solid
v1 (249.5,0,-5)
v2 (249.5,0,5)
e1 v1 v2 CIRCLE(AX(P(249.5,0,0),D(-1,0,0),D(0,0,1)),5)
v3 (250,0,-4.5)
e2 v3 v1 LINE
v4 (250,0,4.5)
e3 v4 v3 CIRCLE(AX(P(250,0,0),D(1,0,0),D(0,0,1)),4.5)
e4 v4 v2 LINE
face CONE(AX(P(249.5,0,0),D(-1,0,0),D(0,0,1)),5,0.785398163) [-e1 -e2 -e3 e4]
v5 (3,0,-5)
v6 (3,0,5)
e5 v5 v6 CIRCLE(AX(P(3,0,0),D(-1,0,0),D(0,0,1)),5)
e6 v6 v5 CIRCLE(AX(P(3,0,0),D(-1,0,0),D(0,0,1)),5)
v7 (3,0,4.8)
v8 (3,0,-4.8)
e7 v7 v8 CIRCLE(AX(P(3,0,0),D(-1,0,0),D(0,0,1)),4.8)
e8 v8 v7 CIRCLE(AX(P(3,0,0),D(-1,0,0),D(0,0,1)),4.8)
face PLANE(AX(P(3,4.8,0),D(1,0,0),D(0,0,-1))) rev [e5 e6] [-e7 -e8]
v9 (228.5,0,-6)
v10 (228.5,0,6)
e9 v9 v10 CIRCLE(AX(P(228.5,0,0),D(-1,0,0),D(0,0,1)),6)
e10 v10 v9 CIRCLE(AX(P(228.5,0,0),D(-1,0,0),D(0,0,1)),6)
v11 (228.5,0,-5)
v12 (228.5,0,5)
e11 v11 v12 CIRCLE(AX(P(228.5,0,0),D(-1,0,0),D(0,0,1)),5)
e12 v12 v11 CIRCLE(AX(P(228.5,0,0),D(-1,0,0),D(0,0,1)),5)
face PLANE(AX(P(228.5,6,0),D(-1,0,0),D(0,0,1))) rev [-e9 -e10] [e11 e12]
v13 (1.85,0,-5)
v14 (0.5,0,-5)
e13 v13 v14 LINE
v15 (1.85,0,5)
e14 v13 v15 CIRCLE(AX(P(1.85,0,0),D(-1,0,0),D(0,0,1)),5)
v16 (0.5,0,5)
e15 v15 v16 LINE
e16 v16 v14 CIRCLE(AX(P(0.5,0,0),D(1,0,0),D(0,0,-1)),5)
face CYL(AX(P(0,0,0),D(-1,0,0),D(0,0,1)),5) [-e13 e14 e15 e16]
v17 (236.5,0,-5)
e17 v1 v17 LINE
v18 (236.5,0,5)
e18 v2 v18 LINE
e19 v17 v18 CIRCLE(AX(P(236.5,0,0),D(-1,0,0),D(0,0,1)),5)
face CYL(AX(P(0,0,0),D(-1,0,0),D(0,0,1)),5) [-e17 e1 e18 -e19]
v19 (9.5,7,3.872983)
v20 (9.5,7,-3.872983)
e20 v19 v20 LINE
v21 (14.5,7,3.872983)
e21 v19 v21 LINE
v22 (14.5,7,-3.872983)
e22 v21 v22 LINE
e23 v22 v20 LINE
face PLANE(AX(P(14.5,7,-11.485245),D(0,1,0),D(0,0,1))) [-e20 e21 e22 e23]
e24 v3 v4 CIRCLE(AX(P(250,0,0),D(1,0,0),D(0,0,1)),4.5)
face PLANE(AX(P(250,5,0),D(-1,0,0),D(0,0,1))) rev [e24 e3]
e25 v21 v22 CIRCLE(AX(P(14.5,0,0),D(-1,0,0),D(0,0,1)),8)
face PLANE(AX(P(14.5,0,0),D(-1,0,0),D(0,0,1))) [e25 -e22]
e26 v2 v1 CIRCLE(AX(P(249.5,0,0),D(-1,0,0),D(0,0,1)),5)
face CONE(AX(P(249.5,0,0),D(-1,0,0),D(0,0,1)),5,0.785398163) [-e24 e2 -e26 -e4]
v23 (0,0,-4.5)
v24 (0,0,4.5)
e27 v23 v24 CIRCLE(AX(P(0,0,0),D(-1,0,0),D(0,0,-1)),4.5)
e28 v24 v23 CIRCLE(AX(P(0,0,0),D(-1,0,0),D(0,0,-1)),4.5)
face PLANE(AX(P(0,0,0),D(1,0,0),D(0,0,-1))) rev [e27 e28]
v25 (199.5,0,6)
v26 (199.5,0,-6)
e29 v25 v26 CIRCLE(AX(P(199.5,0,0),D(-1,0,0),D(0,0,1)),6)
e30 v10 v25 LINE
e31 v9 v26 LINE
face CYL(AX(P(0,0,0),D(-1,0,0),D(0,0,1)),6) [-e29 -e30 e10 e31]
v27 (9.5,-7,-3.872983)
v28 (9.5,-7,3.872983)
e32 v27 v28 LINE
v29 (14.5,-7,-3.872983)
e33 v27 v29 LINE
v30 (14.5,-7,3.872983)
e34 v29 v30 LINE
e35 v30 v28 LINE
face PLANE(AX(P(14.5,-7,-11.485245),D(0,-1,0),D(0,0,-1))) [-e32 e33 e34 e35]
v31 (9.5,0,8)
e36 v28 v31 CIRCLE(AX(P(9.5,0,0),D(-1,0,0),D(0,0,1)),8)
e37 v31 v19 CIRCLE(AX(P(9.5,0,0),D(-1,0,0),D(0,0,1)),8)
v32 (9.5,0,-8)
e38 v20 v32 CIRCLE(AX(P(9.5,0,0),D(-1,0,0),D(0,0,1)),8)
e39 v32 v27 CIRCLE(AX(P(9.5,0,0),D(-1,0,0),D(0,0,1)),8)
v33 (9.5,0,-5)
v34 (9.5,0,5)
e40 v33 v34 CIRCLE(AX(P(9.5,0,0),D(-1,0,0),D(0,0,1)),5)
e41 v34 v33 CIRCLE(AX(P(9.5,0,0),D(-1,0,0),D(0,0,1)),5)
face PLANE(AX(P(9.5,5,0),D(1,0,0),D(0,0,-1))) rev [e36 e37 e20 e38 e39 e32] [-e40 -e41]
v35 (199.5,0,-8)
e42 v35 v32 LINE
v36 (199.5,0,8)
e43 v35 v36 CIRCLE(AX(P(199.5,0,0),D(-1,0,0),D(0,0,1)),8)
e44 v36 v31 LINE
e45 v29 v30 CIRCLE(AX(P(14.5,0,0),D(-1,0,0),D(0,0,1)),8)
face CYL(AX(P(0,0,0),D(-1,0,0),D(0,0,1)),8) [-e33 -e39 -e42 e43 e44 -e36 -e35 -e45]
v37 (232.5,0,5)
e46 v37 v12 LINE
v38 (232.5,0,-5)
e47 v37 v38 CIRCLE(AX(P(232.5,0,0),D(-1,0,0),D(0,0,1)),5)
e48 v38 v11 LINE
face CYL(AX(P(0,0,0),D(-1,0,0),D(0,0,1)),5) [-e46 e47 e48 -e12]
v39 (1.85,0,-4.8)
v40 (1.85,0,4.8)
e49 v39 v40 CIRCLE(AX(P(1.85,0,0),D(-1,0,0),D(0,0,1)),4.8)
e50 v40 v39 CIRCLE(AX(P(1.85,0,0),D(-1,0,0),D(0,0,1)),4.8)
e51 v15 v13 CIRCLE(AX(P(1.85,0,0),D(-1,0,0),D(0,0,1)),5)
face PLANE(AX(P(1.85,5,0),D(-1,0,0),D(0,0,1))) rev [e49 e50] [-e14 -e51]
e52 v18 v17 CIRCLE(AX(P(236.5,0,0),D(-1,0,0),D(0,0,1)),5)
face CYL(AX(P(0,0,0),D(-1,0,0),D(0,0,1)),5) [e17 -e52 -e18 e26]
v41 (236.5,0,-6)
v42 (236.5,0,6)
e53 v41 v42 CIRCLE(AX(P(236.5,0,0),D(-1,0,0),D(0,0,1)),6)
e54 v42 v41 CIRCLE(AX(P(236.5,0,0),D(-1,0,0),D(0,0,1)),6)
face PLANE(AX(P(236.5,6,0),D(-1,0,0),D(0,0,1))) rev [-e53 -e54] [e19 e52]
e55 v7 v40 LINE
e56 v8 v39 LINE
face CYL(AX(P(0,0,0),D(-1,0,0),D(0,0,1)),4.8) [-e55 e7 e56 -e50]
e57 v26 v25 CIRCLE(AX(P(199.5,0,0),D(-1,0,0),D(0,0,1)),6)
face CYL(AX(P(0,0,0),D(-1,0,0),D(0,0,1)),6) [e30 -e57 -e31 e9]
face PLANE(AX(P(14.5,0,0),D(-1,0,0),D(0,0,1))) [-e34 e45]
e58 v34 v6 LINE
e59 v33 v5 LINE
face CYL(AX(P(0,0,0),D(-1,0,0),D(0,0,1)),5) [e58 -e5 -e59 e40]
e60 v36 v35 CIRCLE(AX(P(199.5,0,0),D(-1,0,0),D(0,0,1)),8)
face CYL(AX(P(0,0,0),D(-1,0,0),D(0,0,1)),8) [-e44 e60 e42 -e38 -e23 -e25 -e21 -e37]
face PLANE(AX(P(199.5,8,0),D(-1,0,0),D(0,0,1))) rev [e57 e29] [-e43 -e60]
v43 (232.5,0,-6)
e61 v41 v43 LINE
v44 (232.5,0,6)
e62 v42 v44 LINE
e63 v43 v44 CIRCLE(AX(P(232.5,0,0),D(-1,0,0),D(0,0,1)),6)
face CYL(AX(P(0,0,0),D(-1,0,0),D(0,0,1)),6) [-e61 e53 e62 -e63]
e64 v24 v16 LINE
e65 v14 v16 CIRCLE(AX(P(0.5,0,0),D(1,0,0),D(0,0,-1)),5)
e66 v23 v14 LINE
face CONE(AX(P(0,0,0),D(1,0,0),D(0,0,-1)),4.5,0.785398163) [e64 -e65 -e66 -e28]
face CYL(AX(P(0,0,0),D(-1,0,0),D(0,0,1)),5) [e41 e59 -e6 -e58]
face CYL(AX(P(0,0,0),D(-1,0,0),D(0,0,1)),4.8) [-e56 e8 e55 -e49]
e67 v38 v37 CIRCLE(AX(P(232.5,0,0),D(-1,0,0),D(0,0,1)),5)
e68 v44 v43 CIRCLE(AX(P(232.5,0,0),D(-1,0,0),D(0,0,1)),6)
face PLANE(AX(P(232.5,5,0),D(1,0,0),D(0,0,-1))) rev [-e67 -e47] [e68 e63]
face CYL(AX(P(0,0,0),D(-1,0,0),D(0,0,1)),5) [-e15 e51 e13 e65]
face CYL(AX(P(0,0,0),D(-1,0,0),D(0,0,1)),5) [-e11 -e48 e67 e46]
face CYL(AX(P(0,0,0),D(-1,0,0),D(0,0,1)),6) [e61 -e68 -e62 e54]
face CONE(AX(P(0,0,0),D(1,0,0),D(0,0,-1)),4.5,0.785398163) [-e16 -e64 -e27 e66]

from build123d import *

# Parameters (mm, degrees)
SKETCH2_OUTSIDE_W   = 68.204
SKETCH2_OUTSIDE_H   = 68.204
SKETCH2_OUTSIDE_W_2 = 22.970489672
SKETCH2_OUTSIDE_H_2 = 14
CUT_EXTRUDE1_DEPTH  = 5
CHAMFER1_SIZE       = 0.5


with BuildPart() as part:
    # Sketch1 → Revolve1 (revolve)
    with BuildSketch(Plane.XY, mode=Mode.PRIVATE) as revolve1_sk:
        Polygon((0, 0), (0, 5), (1.85, 5), (1.85, 4.8), (3, 4.8), (3, 5), (9.5, 5), (9.5, 8), (199.5, 8), (199.5, 6), (228.5, 6), (228.5, 5), (232.5, 5), (232.5, 6), (236.5, 6), (236.5, 5), (250, 5), (250, 0), align=None)
    revolve(revolve1_sk.sketch.rotate(Axis((0, 0, 0), (1, 0, 0)), 90), axis=Axis((0, 0, 0), (1, 0, 0)))

    # Sketch2 outside → Cut-Extrude1 (cut)
    with BuildSketch(Plane.ZY.offset(-9.5)):
        Rectangle(SKETCH2_OUTSIDE_W, SKETCH2_OUTSIDE_H)
        Rectangle(SKETCH2_OUTSIDE_W_2, SKETCH2_OUTSIDE_H_2, mode=Mode.SUBTRACT)
    extrude(amount=-CUT_EXTRUDE1_DEPTH, mode=Mode.SUBTRACT)

    # Chamfer1
    chamfer1_edges = [part.edges().sort_by_distance(p)[0] for p in [
        (250, 0, -5),
        (0, 0, -5),
    ]]
    chamfer(chamfer1_edges, length=CHAMFER1_SIZE)


solid = part.part
